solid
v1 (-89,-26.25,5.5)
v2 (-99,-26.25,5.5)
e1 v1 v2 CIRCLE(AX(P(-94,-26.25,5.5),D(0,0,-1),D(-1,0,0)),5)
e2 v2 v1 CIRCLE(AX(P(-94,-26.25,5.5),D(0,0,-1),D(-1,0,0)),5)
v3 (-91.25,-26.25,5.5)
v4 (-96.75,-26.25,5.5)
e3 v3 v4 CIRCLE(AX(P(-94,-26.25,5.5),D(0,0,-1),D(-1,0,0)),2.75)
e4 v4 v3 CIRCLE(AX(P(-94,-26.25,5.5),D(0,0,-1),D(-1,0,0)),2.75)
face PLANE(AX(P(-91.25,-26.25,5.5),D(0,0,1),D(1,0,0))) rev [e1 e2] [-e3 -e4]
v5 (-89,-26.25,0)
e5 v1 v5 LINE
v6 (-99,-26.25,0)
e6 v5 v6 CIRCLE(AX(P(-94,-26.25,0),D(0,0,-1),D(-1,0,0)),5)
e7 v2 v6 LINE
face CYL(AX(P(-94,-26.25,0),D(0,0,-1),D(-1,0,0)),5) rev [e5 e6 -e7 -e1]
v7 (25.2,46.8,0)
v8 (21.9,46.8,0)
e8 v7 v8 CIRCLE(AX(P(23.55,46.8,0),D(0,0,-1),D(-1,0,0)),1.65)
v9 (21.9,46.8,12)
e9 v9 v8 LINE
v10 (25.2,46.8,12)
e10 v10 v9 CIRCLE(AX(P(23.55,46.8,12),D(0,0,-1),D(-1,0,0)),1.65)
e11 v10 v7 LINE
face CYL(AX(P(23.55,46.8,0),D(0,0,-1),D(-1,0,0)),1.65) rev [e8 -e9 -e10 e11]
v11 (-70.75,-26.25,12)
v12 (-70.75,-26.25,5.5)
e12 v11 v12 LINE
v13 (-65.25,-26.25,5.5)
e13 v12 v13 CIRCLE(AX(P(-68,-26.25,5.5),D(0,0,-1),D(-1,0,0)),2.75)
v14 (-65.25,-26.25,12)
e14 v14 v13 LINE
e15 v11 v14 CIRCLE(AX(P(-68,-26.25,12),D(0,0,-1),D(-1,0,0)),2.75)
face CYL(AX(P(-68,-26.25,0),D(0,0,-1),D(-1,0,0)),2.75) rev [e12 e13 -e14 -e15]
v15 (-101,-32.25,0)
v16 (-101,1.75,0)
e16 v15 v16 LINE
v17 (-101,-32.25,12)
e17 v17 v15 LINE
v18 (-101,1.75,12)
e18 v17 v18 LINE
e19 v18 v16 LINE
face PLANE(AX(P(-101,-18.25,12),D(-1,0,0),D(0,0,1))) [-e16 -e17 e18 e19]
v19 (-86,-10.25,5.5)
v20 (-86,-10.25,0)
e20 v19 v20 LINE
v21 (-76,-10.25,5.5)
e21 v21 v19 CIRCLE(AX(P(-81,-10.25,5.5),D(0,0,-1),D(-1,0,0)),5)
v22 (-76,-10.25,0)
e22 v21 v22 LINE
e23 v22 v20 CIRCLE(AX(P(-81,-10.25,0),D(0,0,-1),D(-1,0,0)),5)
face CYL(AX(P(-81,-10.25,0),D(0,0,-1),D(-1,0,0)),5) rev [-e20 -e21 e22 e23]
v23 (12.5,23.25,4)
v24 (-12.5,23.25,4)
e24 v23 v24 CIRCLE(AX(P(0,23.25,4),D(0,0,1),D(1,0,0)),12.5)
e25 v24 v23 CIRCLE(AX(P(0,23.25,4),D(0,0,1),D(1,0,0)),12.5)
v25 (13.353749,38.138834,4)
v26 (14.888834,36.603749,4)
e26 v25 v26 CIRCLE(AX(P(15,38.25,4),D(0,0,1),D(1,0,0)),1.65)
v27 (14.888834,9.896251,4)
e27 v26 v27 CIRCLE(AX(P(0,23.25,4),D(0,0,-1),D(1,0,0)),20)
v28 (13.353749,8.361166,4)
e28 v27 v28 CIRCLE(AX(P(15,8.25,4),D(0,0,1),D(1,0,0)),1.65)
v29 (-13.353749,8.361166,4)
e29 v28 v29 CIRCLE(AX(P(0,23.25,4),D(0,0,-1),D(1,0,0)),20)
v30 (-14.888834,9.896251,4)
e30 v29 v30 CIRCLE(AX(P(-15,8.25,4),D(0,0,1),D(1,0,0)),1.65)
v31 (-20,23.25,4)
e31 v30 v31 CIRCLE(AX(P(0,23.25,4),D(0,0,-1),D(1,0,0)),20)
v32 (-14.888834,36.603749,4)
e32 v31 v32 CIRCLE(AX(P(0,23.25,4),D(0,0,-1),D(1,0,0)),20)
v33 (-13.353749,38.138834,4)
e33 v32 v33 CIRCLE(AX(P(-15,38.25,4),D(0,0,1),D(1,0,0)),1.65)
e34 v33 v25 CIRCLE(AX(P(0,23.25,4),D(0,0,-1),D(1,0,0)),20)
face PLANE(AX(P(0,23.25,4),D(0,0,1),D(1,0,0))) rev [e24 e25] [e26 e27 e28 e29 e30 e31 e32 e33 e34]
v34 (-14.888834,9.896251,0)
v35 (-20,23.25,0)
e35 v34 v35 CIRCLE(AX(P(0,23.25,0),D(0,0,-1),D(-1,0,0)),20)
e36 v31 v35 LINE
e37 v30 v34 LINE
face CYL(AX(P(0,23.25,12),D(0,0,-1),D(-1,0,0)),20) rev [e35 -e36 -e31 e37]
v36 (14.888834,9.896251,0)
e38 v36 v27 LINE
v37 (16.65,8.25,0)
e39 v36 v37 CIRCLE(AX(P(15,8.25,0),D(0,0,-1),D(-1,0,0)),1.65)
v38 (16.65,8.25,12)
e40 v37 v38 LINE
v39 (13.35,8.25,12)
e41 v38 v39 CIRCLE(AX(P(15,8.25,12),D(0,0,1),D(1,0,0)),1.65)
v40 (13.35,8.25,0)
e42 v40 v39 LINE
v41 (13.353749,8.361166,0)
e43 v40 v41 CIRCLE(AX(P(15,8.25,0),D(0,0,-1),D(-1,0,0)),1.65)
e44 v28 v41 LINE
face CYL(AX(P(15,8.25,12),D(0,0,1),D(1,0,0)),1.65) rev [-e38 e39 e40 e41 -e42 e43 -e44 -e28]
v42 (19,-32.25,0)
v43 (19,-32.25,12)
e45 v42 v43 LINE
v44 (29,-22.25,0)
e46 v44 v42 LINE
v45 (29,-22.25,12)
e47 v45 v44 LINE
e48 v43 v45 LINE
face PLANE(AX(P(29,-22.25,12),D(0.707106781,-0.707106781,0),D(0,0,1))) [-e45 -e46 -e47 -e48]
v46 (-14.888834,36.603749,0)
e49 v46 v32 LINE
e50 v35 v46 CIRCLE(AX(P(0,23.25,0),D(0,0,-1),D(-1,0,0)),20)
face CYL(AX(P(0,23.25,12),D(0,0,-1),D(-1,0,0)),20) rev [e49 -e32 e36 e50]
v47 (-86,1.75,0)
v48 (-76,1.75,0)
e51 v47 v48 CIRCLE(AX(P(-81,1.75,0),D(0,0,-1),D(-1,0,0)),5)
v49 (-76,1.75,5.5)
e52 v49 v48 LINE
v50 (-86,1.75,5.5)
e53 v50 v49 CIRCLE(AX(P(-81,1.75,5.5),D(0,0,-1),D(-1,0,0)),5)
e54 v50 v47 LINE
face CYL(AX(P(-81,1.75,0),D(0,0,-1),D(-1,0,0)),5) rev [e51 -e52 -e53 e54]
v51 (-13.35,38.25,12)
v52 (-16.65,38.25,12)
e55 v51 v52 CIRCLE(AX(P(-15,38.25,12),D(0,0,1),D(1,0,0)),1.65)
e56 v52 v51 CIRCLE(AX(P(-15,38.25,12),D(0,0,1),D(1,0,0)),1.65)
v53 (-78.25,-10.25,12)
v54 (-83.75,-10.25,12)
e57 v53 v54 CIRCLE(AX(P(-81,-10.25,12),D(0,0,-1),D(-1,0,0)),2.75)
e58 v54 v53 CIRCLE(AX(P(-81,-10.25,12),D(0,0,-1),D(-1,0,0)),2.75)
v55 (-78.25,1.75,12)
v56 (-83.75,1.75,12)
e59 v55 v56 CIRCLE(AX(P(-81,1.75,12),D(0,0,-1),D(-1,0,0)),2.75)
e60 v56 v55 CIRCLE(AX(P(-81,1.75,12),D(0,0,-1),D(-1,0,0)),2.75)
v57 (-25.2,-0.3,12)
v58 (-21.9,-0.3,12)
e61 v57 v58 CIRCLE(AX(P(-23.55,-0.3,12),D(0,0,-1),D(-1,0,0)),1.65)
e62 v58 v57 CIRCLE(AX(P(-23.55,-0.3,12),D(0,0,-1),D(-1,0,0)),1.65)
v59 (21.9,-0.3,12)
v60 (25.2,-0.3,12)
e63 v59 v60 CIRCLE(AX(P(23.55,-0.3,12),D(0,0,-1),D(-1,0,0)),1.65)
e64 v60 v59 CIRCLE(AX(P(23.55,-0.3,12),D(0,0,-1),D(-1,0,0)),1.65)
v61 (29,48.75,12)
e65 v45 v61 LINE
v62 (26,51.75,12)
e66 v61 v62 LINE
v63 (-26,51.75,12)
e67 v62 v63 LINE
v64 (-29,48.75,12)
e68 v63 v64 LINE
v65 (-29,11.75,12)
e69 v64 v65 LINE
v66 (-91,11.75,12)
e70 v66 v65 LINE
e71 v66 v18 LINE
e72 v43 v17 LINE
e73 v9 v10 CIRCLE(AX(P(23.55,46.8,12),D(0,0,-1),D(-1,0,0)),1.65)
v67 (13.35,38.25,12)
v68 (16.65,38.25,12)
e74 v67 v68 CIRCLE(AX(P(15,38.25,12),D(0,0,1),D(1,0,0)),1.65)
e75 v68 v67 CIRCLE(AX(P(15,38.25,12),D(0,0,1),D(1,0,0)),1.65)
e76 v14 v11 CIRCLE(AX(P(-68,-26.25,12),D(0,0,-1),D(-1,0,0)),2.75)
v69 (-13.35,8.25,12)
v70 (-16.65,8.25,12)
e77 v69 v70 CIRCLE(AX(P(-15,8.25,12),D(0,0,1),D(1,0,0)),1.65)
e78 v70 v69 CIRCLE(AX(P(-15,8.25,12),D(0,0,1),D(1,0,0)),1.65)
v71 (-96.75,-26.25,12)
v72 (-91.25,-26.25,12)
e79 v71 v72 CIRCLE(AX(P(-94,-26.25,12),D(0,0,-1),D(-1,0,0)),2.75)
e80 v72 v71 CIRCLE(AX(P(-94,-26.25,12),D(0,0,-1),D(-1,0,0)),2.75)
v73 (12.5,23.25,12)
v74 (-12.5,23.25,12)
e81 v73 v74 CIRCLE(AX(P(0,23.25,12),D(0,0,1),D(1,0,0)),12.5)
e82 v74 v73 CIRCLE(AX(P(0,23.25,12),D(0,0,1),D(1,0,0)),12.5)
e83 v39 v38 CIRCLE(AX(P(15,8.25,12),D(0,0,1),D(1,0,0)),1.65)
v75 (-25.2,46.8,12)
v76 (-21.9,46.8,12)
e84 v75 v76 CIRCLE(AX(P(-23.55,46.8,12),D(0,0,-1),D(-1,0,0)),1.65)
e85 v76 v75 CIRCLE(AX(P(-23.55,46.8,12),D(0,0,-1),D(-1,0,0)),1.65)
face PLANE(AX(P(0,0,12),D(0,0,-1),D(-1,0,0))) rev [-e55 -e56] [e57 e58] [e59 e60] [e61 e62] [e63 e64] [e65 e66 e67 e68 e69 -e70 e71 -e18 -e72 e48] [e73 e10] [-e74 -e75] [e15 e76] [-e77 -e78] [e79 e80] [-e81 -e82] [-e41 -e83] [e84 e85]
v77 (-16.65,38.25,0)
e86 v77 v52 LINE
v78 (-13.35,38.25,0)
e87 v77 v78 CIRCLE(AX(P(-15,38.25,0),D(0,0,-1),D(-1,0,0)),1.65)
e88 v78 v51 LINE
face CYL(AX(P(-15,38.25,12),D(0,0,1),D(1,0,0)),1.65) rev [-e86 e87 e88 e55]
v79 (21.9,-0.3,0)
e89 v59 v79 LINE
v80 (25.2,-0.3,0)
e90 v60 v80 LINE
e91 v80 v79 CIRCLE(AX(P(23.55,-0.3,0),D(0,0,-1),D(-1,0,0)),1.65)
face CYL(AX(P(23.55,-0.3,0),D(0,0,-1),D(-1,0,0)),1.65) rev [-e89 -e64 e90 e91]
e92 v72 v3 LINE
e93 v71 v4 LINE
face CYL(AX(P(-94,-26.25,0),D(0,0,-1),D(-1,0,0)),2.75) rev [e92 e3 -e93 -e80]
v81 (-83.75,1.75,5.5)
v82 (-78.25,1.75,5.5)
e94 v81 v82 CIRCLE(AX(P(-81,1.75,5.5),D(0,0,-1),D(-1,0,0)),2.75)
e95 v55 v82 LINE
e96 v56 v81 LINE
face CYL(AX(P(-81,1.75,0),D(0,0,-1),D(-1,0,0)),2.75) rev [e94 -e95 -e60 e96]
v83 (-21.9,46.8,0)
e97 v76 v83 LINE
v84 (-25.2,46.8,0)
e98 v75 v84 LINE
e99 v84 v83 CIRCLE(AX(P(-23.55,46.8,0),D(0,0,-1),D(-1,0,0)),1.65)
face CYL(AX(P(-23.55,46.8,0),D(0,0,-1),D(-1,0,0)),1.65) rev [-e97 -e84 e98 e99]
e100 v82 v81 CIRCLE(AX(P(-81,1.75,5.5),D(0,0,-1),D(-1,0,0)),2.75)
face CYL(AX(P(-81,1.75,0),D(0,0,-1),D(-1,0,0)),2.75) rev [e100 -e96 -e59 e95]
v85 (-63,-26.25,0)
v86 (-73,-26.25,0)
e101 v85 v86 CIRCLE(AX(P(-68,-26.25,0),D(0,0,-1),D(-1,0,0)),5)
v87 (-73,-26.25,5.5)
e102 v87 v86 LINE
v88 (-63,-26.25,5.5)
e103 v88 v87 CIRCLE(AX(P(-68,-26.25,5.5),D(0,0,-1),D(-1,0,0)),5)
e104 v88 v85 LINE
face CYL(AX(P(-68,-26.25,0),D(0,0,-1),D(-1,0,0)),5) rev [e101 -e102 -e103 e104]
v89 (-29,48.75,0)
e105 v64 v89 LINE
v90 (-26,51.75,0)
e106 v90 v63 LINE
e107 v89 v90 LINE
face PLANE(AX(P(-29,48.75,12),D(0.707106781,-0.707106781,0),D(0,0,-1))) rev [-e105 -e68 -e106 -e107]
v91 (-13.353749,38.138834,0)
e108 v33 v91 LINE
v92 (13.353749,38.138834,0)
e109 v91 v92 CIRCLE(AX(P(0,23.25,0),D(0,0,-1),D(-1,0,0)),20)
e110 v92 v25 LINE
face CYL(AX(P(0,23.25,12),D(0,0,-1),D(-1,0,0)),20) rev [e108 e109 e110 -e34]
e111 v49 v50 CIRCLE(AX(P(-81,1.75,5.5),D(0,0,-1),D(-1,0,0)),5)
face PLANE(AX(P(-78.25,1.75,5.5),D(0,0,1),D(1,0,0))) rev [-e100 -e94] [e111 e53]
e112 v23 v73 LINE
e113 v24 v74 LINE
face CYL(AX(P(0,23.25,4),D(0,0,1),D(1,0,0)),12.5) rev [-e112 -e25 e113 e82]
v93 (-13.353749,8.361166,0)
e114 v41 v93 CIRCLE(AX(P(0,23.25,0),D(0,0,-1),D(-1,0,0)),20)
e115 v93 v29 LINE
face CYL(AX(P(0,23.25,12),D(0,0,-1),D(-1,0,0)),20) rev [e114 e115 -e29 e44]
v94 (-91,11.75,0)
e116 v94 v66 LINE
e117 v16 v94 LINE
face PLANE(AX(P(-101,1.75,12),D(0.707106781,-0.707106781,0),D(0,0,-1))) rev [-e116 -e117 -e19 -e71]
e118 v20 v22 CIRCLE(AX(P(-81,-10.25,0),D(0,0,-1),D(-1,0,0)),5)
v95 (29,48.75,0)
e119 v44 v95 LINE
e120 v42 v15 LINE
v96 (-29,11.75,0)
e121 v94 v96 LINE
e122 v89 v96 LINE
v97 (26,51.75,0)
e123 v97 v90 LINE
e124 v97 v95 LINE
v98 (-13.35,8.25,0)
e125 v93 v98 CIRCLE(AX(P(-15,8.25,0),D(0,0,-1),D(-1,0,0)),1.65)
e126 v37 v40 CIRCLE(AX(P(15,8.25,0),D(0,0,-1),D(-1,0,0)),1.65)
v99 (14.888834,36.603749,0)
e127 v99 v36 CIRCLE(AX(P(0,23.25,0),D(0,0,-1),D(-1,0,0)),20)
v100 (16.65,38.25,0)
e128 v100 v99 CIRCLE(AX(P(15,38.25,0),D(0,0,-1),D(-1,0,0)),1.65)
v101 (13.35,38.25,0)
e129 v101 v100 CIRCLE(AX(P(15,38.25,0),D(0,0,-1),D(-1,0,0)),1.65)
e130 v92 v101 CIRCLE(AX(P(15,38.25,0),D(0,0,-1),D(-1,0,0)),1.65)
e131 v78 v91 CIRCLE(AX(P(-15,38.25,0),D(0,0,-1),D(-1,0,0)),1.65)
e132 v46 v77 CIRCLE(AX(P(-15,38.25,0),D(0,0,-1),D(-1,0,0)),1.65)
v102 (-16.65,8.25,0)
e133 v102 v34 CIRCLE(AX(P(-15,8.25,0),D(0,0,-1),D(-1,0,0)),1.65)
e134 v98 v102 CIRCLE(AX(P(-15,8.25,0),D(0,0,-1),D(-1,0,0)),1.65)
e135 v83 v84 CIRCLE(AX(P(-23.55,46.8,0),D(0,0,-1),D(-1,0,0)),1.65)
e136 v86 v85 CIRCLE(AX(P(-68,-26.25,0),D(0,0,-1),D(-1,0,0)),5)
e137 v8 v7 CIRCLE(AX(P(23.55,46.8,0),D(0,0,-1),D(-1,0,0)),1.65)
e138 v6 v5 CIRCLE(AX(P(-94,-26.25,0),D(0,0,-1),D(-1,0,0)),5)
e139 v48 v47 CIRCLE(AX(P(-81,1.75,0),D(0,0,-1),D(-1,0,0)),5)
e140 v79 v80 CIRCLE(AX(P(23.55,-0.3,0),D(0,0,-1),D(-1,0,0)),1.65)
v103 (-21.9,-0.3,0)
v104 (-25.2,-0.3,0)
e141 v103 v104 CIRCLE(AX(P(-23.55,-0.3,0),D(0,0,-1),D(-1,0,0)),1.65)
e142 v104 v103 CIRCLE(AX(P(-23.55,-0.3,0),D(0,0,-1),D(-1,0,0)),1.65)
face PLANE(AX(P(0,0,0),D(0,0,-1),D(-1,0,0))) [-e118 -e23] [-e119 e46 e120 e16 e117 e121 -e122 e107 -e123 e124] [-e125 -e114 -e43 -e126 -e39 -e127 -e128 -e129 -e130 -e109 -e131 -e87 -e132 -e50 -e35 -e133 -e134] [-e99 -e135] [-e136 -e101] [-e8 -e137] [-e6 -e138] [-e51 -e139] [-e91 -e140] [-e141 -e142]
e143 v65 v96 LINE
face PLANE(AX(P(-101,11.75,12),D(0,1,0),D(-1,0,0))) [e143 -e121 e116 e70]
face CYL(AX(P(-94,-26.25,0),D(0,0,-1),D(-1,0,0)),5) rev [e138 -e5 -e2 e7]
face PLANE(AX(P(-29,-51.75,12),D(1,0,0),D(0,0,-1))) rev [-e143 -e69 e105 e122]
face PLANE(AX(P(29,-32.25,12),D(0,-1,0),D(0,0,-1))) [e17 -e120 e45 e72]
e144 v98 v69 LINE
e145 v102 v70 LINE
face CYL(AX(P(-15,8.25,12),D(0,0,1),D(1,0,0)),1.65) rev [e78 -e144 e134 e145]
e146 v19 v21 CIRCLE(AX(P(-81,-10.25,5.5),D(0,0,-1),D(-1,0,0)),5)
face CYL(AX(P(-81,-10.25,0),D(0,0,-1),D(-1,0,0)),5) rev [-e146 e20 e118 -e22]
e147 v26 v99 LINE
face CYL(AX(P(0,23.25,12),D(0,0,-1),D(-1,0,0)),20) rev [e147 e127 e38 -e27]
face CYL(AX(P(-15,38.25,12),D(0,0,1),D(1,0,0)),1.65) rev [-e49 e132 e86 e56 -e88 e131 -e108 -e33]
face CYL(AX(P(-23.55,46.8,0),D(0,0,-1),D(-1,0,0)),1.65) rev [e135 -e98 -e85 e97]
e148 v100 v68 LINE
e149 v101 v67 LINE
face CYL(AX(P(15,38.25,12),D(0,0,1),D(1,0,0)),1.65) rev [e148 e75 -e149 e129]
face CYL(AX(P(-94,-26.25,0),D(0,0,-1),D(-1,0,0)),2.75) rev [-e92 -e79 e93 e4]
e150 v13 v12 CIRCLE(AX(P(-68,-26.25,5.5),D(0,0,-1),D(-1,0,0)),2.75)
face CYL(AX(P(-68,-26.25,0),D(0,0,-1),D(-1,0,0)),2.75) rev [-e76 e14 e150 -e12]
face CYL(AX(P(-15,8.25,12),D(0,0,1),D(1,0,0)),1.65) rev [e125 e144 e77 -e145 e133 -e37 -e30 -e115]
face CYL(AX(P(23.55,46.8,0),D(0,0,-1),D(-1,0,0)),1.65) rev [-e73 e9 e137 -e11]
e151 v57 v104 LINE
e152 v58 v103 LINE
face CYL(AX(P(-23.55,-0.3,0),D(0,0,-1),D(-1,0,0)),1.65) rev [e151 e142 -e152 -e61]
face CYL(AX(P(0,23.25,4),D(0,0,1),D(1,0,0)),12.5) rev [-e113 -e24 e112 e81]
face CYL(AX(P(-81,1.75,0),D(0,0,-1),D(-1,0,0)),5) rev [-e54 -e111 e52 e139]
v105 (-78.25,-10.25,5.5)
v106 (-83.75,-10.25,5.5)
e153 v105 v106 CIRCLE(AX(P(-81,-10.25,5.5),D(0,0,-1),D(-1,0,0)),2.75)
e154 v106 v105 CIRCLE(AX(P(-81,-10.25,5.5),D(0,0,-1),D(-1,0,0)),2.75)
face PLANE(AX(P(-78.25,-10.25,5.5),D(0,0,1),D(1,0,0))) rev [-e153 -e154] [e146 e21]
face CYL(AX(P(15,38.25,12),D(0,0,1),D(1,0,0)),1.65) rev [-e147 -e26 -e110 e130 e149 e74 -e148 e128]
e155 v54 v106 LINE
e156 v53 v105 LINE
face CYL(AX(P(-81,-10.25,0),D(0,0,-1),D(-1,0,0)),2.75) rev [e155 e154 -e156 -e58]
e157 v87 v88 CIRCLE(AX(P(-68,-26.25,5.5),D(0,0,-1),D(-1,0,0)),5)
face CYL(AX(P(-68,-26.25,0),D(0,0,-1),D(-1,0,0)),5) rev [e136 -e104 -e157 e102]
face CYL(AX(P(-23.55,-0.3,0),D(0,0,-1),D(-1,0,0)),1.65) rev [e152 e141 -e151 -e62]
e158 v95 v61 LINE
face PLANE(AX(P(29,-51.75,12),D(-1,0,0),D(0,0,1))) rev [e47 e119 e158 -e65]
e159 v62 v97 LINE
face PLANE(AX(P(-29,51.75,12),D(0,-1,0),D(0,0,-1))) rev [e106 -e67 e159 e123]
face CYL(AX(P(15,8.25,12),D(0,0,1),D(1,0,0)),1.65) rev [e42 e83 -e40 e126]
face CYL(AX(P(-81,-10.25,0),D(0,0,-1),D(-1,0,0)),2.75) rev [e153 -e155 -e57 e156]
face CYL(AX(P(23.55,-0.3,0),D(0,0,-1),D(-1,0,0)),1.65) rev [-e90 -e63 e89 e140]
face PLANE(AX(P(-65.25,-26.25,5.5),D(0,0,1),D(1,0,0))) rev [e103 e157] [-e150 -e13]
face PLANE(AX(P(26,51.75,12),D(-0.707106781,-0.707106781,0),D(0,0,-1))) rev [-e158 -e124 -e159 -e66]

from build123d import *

# Parameters (mm, degrees)
SKETCH_1_W                  = 58
SKETCH_1_H                  = 103.5
EXTRUDE_1_DEPTH             = 12
HOLE_WIZARD_M4_1_D          = 3.3
SKETCH_5_R                  = 20
CUT_EXTRUDE_1_DEPTH         = 61.523239338
SKETCH_6_W                  = 58
SKETCH_6_H                  = 58
EXTRUDE_2_DEPTH             = 10
SKETCH_10_W                 = 48
SKETCH_10_H                 = 10
CUT_EXTRUDE_2_DEPTH         = 146
CHAMFER_1_SIZE              = 3
CUT_EXTRUDE_5_DEPTH         = 86.56320763
CUT_EXTRUDE_5_DEPTH_BACK    = 86.56320763
SKETCH_15_W                 = 130
SKETCH_15_H                 = 14
EXTRUDE_3_DEPTH             = 12
SKETCH_16_W                 = 40
SKETCH_16_H                 = 14
EXTRUDE_4_DEPTH             = 60
EXTRUDE_START               = -40
SKETCH_17_W                 = 12
SKETCH_17_H                 = 100
EXTRUDE_5_DEPTH             = 40
EXTRUDE_START_2             = -12
SKETCH_18_W                 = 72
SKETCH_18_H                 = 30
EXTRUDE_6_DEPTH             = 12
CHAMFER_2_SIZE              = 10
SKETCH_19_R                 = 22.248352005
SKETCH_19_R_2               = 12.5
EXTRUDE_7_DEPTH             = 8
CUT_EXTRUDE_6_DEPTH         = 158.012738337
CUT_EXTRUDE_6_DEPTH_BACK    = 158.012738337
HOLE_WIZARD_C_0_D           = 5.5
HOLE_WIZARD_C_0_CBORE_D     = 10
HOLE_WIZARD_C_0_CBORE_DEPTH = 5.5
CHAMFER_3_SIZE              = 10
HOLE_WIZARD_M4_2_D          = 3.3


with BuildPart() as part:
    # 草图1 → 凸台-拉伸1 (new body)
    with BuildSketch(Plane.XY):
        Rectangle(SKETCH_1_W, SKETCH_1_H)
    extrude(amount=EXTRUDE_1_DEPTH)

    # M4 螺纹孔1 (through all)
    with Locations(Plane(origin=(0, 0, 0), x_dir=(-1, 0, 0), z_dir=(0, 0, -1))):
        with Locations((-23.55, 46.8), (23.55, 46.8), (23.55, -0.3), (-23.55, -0.3)):
            Hole(HOLE_WIZARD_M4_1_D / 2)

    # 草图5 → 切除-拉伸1 (cut, through all)
    with BuildSketch(Plane(origin=(0, 0, 0), x_dir=(-1, 0, 0), z_dir=(0, 0, -1))):
        with Locations((0, 23.25)):
            Circle(SKETCH_5_R)
    extrude(amount=-CUT_EXTRUDE_1_DEPTH, mode=Mode.SUBTRACT)

    # 草图6 → 凸台-拉伸2 (add)
    with BuildSketch(Plane.XZ.offset(51.75)):
        with Locations((0, 29)):
            Rectangle(SKETCH_6_W, SKETCH_6_H)
    extrude(amount=EXTRUDE_2_DEPTH)

    # 草图10 → 切除-拉伸2 (cut)
    with BuildSketch(Plane(origin=(29, 0, 0), x_dir=(0, 0, -1), z_dir=(1, 0, 0))):
        with Locations((-36, -56.75)):
            Rectangle(SKETCH_10_W, SKETCH_10_H)
    extrude(amount=-CUT_EXTRUDE_2_DEPTH, mode=Mode.SUBTRACT)

    # 倒角1
    chamfer_1_edges = [part.edges().sort_by_distance(p)[0] for p in [
        (29, -61.75, 6),
        (-29, -61.75, 6),
        (-29, 51.75, 6),
        (29, 51.75, 6),
    ]]
    chamfer(chamfer_1_edges, length=CHAMFER_1_SIZE)

    # 草图14 → 切除-拉伸5 (cut, two sides: drawn at the far end of the back side and taken through both)
    with BuildSketch(Plane.ZY.offset(29).offset(-CUT_EXTRUDE_5_DEPTH_BACK)):
        Polygon((-205.249277876, -18.25), (-30, -18.25), (43.895682699, -18.25), (219.144960575, -18.25), (219.144960575, -368.748555752), (-205.249277876, -368.748555752), align=None)
    extrude(amount=CUT_EXTRUDE_5_DEPTH + CUT_EXTRUDE_5_DEPTH_BACK, mode=Mode.SUBTRACT)

    # 草图15 → 凸台-拉伸3 (add)
    with BuildSketch(Plane(origin=(0, 0, 0), x_dir=(-1, 0, 0), z_dir=(0, 0, -1))):
        with Locations((36, -25.25)):
            Rectangle(SKETCH_15_W, SKETCH_15_H)
    extrude(amount=-EXTRUDE_3_DEPTH)

    # 草图16 → 凸台-拉伸4 (add)
    with BuildSketch(Plane.XY.offset(12)):
        with Locations((-81, -25.25)):
            Rectangle(SKETCH_16_W, SKETCH_16_H)
    extrude(amount=EXTRUDE_4_DEPTH)

    # 草图17 → 凸台-拉伸5 (add)
    with BuildSketch(Plane.ZY.offset(101).offset(EXTRUDE_START)):
        with Locations((78, -68.25)):
            Rectangle(SKETCH_17_W, SKETCH_17_H)
    extrude(amount=EXTRUDE_5_DEPTH)

    # 草图18 → 凸台-拉伸6 (add)
    with BuildSketch(Plane(origin=(0, 0, 0), x_dir=(-1, 0, 0), z_dir=(0, 0, -1)).offset(EXTRUDE_START_2)):
        with Locations((65, -3.25)):
            Rectangle(SKETCH_18_W, SKETCH_18_H)
    extrude(amount=EXTRUDE_6_DEPTH)

    # 倒角2
    chamfer_2_edges = [part.edges().sort_by_distance(p)[0] for p in [
        (29, -32.25, 6),
    ]]
    chamfer(chamfer_2_edges, length=CHAMFER_2_SIZE)

    # 草图19 → 凸台-拉伸7 (add)
    with BuildSketch(Plane.XY.offset(12)):
        with Locations((0, 23.25)):
            Circle(SKETCH_19_R)
        with Locations((0, 23.25)):
            Circle(SKETCH_19_R_2, mode=Mode.SUBTRACT)
    extrude(amount=-EXTRUDE_7_DEPTH)

    # 草图20 → 切除-拉伸6 (cut, two sides: drawn at the far end of the back side and taken through both)
    with BuildSketch(Plane.XZ.offset(32.25).offset(-CUT_EXTRUDE_6_DEPTH_BACK)):
        Polygon((259.644501793, 12), (-52.844544679, 12), (-104.007164502, 12), (-416.496210973, 12), (-416.496210973, 636.978092943), (259.644501793, 636.978092943), align=None)
    extrude(amount=CUT_EXTRUDE_6_DEPTH + CUT_EXTRUDE_6_DEPTH_BACK, mode=Mode.SUBTRACT)

    # 打孔尺寸根据六角头螺栓 C 级的类型0 (through all)
    with Locations(Plane(origin=(0, 0, 0), x_dir=(-1, 0, 0), z_dir=(0, 0, -1))):
        with Locations((72.148493823, 215.242463417), (94, -26.25), (68, -26.25), (81, -10.25), (81, 1.75)):
            CounterBoreHole(HOLE_WIZARD_C_0_D / 2, HOLE_WIZARD_C_0_CBORE_D / 2, HOLE_WIZARD_C_0_CBORE_DEPTH)

    # 倒角3
    chamfer_3_edges = [part.edges().sort_by_distance(p)[0] for p in [
        (-101, 11.75, 6),
    ]]
    chamfer(chamfer_3_edges, length=CHAMFER_3_SIZE)

    # M4 螺纹孔2 (through all)
    with Locations(Plane.XY.offset(12)):
        with Locations((15, 8.25), (-15, 8.25), (-15, 38.25), (15, 38.25)):
            Hole(HOLE_WIZARD_M4_2_D / 2)


solid = part.part
